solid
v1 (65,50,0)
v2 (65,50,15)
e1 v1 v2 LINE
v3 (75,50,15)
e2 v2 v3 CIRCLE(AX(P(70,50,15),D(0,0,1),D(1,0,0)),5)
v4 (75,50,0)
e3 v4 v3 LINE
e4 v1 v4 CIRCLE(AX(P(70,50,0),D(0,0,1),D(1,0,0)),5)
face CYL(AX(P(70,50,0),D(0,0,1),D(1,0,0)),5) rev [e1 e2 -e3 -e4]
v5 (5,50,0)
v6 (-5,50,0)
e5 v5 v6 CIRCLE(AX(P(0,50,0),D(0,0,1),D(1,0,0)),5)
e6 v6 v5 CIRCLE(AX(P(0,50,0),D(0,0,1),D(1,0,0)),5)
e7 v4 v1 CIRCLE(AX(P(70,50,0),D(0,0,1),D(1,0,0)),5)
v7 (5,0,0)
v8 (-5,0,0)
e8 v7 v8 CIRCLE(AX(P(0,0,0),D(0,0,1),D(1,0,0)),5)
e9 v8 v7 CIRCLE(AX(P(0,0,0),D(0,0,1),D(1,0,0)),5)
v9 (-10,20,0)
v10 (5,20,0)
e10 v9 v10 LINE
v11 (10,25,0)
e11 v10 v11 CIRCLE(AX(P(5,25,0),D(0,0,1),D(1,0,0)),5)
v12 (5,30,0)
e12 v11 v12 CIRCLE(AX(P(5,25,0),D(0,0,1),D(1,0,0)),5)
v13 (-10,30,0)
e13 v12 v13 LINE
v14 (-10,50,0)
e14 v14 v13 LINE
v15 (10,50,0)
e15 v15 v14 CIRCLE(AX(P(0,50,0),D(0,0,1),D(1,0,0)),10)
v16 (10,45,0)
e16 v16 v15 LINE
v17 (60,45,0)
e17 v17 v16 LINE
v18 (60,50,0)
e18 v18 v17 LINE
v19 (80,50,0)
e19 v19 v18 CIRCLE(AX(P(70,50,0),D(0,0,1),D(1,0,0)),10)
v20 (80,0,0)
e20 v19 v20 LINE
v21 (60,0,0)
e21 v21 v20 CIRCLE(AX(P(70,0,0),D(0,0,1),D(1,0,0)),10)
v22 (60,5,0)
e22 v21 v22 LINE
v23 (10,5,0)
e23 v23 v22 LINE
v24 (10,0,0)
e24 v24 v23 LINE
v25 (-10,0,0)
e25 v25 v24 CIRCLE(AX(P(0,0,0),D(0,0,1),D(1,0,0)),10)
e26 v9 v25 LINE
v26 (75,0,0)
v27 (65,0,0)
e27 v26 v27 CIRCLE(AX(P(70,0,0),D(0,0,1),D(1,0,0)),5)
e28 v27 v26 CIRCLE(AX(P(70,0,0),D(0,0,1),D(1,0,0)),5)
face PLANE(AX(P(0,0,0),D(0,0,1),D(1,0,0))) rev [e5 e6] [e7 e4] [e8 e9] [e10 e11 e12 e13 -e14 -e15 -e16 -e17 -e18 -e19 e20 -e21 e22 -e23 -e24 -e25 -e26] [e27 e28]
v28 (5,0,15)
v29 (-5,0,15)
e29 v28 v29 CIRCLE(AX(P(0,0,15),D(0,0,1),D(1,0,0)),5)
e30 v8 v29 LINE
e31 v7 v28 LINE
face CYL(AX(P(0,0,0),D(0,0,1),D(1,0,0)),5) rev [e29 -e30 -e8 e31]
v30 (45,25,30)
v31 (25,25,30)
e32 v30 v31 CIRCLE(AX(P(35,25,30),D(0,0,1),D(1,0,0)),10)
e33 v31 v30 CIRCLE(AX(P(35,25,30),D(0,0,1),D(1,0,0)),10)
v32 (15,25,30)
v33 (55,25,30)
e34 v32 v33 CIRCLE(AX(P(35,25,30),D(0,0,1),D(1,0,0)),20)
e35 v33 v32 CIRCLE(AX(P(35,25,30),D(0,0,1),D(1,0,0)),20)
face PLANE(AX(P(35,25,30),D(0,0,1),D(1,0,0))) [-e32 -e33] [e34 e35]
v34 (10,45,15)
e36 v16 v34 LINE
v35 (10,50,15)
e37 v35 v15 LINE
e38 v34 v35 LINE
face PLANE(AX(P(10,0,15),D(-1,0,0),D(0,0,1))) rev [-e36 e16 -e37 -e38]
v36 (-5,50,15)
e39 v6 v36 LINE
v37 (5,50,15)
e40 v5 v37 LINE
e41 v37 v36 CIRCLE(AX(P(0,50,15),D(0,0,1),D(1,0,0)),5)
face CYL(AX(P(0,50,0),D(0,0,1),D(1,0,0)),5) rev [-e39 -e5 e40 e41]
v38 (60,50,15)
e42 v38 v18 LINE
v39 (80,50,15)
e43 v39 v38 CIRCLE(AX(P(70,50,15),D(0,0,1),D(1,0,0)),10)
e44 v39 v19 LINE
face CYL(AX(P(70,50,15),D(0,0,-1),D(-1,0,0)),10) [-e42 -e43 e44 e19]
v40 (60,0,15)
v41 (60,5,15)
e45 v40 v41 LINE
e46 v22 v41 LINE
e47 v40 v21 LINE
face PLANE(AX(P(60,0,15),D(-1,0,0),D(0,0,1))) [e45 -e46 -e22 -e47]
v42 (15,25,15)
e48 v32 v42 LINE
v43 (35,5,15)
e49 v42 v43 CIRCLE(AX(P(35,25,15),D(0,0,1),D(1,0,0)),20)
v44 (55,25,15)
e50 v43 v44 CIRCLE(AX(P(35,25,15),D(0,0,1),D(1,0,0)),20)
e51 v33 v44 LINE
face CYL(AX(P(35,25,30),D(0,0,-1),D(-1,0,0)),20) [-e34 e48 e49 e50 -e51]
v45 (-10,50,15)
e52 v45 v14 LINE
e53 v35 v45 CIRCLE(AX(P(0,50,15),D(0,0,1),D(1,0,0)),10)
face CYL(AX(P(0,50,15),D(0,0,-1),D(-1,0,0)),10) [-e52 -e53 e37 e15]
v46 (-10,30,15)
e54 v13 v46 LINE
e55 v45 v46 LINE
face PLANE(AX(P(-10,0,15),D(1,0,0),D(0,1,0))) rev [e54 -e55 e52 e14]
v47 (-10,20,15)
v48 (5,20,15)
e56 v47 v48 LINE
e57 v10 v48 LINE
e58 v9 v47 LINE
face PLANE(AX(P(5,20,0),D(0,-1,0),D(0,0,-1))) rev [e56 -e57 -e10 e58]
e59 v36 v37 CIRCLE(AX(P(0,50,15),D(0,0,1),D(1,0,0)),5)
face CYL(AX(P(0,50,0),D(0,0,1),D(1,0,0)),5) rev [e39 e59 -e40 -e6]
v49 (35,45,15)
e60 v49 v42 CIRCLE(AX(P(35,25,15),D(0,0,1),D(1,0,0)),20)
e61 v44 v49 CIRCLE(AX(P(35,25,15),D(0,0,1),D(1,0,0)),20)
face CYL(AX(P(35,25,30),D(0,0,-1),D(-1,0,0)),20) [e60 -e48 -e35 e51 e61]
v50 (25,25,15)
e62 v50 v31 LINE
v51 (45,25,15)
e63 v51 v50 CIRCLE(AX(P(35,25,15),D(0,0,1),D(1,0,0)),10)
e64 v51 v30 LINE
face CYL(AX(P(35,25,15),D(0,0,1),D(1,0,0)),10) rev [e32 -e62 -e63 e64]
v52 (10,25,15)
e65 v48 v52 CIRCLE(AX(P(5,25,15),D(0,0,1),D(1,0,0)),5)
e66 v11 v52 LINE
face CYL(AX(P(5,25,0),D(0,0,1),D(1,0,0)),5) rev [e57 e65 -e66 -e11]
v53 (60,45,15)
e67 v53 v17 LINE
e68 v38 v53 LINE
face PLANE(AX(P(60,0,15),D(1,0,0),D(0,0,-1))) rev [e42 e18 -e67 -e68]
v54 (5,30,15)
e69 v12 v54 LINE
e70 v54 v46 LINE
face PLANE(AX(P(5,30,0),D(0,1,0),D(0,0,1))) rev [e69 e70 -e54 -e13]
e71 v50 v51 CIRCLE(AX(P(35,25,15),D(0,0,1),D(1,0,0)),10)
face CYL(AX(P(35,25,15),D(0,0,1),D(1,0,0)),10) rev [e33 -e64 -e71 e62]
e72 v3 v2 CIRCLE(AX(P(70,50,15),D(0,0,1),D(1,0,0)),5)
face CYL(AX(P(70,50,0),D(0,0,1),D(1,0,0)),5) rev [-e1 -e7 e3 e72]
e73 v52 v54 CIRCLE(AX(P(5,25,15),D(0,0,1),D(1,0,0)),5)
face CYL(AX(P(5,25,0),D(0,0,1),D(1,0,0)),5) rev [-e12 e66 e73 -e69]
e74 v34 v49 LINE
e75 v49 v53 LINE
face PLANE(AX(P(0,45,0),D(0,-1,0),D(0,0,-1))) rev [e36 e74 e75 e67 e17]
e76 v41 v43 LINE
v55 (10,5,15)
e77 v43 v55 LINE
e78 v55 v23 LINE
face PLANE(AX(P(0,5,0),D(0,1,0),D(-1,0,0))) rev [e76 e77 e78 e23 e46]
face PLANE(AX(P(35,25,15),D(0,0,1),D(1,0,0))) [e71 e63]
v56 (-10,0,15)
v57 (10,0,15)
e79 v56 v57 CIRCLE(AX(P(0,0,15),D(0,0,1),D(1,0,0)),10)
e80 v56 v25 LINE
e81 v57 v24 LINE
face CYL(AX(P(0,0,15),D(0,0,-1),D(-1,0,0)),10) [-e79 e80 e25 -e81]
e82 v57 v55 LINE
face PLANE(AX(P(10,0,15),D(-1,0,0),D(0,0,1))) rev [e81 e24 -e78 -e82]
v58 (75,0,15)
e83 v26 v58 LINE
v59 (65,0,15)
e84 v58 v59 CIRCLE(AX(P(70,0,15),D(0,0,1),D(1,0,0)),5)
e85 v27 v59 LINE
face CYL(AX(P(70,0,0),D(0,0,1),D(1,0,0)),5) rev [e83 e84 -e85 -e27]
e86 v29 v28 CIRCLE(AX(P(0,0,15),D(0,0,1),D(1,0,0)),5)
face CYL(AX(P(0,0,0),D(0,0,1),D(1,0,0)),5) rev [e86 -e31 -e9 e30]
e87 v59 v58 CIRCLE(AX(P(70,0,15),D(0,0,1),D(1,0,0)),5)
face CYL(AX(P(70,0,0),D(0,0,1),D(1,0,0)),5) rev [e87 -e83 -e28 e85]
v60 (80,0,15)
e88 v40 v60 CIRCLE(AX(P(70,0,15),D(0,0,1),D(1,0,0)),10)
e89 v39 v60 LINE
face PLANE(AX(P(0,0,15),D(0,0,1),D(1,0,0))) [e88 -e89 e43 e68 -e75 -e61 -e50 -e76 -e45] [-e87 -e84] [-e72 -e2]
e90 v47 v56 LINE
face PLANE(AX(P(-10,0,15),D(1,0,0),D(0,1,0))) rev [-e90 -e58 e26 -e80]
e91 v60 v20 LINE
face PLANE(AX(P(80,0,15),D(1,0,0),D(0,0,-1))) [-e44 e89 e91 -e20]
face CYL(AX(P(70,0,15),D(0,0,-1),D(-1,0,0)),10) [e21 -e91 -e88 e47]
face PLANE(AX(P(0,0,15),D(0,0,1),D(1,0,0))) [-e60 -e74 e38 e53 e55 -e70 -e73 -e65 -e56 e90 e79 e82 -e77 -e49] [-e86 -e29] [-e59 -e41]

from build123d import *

# Parameters (mm, degrees)
BASE_PLATE_DEPTH           = 15
END_PAD_1_SKETCH_W         = 50
END_PAD_1_SKETCH_H         = 15
END_PAD_1_DEPTH            = 5
END_PAD_2_SKETCH_W         = 50
END_PAD_2_SKETCH_H         = 15
END_PAD_2_DEPTH            = 5
HUB_SKETCH_R               = 20
HUB_40_DEPTH               = 15
BORE_SKETCH_R              = 10
BORE_20_DEPTH              = 15
MOUNTING_HOLES_SKETCH_R    = 5
MOUNTING_HOLES_4X_10_DEPTH = 15
SIDE_NOTCH_DEPTH           = 15


with BuildPart() as part:
    # Base Plate Sketch → Base Plate (new body)
    with BuildSketch(Plane.XY):
        with BuildLine():
            Line((-10, 50), (-10, 0))
            ThreePointArc((-10, 0), (0, -10), (10, 0))
            Line((10, 0), (10, 10))
            Line((10, 10), (60, 10))
            Line((60, 10), (60, 0))
            ThreePointArc((60, 0), (70, -10), (80, 0))
            Line((80, 0), (80, 50))
            ThreePointArc((80, 50), (70, 60), (60, 50))
            Line((60, 50), (60, 40))
            Line((60, 40), (10, 40))
            Line((10, 40), (10, 50))
            ThreePointArc((10, 50), (0, 60), (-10, 50))
        make_face()
    extrude(amount=BASE_PLATE_DEPTH)

    # End Pad 1 Sketch → End Pad 1 (add)
    with BuildSketch(Plane(origin=(0, 40, 0), x_dir=(1, 0, 0), z_dir=(0, 1, 0))):
        with Locations((35, -7.5)):
            Rectangle(END_PAD_1_SKETCH_W, END_PAD_1_SKETCH_H)
    extrude(amount=END_PAD_1_DEPTH)

    # End Pad 2 Sketch → End Pad 2 (add)
    with BuildSketch(Plane.XZ.offset(-10)):
        with Locations((35, 7.5)):
            Rectangle(END_PAD_2_SKETCH_W, END_PAD_2_SKETCH_H)
    extrude(amount=END_PAD_2_DEPTH)

    # Hub Sketch → Hub Ø40 (add)
    with BuildSketch(Plane.XY.offset(15)):
        with Locations(Location((35, 25, 0), (0, 0, 270))):
            Circle(HUB_SKETCH_R)
    extrude(amount=HUB_40_DEPTH)

    # Bore Sketch → Bore Ø20 (cut)
    with BuildSketch(Plane.XY.offset(30)):
        with Locations((35, 25)):
            Circle(BORE_SKETCH_R)
    extrude(amount=-BORE_20_DEPTH, mode=Mode.SUBTRACT)

    # Mounting Holes Sketch → Mounting Holes 4xØ10 (cut)
    with BuildSketch(Plane.XY.offset(15)):
        with Locations((70, 50)):
            Circle(MOUNTING_HOLES_SKETCH_R)
        with Locations((70, 0)):
            Circle(MOUNTING_HOLES_SKETCH_R)
        Circle(MOUNTING_HOLES_SKETCH_R)
        with Locations((0, 50)):
            Circle(MOUNTING_HOLES_SKETCH_R)
    extrude(amount=-MOUNTING_HOLES_4X_10_DEPTH, mode=Mode.SUBTRACT)

    # Side Notch Sketch → Side Notch (cut)
    with BuildSketch(Plane.XY.offset(15)):
        with BuildLine():
            Line((-10, 30), (-10, 20))
            Line((-10, 20), (5, 20))
            ThreePointArc((5, 20), (10, 25), (5, 30))
            Line((5, 30), (-10, 30))
        make_face()
    extrude(amount=-SIDE_NOTCH_DEPTH, mode=Mode.SUBTRACT)


solid = part.part
